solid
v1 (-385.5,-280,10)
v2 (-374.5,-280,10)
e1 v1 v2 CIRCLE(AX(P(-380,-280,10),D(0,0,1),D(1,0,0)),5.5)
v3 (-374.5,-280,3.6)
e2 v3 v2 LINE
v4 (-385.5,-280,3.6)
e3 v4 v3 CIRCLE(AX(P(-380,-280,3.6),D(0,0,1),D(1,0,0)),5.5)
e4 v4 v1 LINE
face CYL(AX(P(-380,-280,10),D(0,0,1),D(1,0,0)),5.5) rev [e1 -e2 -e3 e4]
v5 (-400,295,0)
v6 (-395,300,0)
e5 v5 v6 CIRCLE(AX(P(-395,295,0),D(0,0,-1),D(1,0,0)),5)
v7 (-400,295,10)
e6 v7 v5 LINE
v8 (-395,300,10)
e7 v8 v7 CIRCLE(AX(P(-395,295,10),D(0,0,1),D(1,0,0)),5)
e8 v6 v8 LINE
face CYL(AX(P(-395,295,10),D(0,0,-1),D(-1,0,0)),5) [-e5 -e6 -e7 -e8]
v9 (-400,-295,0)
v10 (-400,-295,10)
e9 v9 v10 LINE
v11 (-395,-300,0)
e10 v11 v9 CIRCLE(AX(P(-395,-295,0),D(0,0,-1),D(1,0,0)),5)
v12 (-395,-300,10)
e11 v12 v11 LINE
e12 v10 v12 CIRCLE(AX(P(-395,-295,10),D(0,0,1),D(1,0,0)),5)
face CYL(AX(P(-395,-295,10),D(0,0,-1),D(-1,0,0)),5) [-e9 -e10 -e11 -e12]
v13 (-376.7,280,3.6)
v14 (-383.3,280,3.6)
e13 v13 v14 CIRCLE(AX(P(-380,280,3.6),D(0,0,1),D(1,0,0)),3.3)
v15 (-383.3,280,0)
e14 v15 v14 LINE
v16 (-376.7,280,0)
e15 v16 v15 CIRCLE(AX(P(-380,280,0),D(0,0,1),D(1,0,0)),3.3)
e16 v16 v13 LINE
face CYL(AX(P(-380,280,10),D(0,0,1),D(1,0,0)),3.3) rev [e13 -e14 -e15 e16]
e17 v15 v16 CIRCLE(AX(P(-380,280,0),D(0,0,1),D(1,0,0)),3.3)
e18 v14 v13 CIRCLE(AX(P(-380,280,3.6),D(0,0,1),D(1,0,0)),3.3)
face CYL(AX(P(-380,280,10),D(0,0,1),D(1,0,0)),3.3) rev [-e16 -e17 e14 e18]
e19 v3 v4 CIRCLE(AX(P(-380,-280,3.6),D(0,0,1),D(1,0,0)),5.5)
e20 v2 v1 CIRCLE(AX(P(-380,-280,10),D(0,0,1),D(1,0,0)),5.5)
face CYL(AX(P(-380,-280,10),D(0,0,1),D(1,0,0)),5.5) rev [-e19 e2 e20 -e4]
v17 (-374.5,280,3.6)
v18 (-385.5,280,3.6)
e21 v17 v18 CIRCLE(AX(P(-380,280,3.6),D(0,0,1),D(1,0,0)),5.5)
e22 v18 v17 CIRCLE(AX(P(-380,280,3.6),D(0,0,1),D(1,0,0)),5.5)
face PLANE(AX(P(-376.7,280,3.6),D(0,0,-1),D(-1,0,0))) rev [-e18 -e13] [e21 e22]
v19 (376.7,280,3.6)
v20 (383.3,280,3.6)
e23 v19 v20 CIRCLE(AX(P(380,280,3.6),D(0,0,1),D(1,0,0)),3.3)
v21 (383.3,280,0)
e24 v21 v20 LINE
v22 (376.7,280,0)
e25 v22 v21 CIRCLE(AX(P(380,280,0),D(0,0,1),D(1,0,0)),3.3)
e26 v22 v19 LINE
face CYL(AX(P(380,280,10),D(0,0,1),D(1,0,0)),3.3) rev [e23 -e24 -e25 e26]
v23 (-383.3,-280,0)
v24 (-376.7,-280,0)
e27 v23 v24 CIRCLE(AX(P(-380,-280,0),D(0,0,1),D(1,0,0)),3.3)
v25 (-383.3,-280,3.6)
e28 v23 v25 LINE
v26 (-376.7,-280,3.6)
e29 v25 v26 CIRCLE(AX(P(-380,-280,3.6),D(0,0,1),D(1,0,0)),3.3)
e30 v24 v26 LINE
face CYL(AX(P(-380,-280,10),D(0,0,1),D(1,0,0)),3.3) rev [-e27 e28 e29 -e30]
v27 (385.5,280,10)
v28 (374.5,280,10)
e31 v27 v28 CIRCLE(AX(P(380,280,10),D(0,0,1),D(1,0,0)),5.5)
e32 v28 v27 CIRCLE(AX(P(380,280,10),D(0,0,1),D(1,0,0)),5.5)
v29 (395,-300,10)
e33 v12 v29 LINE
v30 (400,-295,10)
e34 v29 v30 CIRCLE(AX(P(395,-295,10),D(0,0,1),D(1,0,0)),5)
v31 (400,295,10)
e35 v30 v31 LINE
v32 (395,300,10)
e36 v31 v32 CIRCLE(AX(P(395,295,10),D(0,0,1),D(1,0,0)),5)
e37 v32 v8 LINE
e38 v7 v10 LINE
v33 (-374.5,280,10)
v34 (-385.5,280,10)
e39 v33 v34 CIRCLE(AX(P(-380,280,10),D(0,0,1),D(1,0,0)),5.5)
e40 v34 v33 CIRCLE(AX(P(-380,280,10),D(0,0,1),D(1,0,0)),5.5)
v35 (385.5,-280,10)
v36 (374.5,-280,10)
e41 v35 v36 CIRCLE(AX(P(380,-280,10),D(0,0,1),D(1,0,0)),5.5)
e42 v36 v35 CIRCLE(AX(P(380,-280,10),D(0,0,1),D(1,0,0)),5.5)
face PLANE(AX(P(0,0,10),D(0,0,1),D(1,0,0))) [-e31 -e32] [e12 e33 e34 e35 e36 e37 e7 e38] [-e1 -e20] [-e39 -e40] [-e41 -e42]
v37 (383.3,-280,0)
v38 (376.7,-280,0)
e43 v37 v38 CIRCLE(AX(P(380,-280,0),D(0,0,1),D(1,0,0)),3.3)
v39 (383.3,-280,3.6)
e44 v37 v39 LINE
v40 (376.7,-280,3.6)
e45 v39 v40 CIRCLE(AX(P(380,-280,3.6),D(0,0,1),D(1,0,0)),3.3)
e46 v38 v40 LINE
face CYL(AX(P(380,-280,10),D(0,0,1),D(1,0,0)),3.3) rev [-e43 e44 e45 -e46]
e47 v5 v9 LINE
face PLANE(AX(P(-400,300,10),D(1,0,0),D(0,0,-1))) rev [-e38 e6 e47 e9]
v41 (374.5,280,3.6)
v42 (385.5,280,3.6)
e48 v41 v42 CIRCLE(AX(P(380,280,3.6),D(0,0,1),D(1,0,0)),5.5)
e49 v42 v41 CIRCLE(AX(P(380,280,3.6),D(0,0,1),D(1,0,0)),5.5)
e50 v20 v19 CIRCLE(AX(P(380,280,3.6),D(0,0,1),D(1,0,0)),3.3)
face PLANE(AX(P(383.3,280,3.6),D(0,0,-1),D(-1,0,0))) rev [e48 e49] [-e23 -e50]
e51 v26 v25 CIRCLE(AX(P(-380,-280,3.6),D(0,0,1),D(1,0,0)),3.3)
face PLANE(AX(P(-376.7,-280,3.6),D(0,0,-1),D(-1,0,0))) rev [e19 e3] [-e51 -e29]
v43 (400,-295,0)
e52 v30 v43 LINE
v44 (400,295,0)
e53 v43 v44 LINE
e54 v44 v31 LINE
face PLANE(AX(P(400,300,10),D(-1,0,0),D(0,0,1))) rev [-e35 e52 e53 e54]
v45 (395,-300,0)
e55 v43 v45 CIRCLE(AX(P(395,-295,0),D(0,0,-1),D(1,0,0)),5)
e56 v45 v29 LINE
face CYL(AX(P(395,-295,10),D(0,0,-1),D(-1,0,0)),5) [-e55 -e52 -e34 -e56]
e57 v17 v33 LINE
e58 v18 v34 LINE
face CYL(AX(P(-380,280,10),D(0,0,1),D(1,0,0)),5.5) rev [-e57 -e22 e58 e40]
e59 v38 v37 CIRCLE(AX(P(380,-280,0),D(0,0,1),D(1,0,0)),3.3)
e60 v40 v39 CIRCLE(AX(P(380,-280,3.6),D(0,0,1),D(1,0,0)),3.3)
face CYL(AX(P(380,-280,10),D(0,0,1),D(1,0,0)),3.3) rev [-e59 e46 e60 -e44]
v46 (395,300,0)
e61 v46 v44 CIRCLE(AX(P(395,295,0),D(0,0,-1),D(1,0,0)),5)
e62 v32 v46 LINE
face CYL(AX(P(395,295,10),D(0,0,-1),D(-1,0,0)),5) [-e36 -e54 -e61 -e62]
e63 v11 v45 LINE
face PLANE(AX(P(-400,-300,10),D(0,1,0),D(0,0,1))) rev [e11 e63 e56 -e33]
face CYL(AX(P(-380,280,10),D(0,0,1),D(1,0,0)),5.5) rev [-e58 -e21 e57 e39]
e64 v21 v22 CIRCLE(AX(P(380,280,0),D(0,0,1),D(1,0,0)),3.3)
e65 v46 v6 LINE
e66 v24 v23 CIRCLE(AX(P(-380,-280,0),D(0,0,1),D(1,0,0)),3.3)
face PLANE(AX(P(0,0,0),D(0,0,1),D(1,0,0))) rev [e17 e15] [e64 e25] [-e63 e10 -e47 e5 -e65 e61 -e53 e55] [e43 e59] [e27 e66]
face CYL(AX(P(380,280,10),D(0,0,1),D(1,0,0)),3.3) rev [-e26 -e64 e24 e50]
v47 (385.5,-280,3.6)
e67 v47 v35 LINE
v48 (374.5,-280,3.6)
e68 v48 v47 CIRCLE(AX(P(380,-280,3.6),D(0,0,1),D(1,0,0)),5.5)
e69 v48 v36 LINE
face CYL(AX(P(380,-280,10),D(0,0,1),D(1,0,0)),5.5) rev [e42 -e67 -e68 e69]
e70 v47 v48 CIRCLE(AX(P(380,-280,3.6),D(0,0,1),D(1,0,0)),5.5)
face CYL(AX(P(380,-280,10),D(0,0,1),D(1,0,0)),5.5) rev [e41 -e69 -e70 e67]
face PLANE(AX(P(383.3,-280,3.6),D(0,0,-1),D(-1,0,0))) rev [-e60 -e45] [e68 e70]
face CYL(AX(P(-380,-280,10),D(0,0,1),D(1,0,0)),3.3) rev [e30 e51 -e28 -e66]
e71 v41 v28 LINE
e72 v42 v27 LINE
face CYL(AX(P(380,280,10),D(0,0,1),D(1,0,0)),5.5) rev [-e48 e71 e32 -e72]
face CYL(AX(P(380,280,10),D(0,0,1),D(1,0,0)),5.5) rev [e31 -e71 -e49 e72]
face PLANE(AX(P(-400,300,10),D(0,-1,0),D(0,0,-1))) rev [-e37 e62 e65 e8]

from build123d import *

# Parameters (mm, degrees)
SKETCH_1_W                   = 800
SKETCH_1_H                   = 600
EXTRUDE_1_DEPTH              = 10
HOLE_WIZARD_M6_1_D           = 6.6
HOLE_WIZARD_M6_1_CBORE_D     = 11
HOLE_WIZARD_M6_1_CBORE_DEPTH = 6.4
FILLET_1_R                   = 5


with BuildPart() as part:
    # 草图1 → 凸台-拉伸1 (new body)
    with BuildSketch(Plane.XY):
        Rectangle(SKETCH_1_W, SKETCH_1_H)
    extrude(amount=EXTRUDE_1_DEPTH)

    # M6 六角凹头螺钉的柱形沉头孔1 (through all)
    with Locations(Plane.XY.offset(10)):
        with Locations((-380, 280), (380, 280), (380, -280), (-380, -280)):
            CounterBoreHole(HOLE_WIZARD_M6_1_D / 2, HOLE_WIZARD_M6_1_CBORE_D / 2, HOLE_WIZARD_M6_1_CBORE_DEPTH)

    # 圆角1
    fillet_1_edges = [part.edges().sort_by_distance(p)[0] for p in [
        (400, -300, 5),
        (-400, -300, 5),
        (-400, 300, 5),
        (400, 300, 5),
    ]]
    fillet(fillet_1_edges, radius=FILLET_1_R)


solid = part.part
